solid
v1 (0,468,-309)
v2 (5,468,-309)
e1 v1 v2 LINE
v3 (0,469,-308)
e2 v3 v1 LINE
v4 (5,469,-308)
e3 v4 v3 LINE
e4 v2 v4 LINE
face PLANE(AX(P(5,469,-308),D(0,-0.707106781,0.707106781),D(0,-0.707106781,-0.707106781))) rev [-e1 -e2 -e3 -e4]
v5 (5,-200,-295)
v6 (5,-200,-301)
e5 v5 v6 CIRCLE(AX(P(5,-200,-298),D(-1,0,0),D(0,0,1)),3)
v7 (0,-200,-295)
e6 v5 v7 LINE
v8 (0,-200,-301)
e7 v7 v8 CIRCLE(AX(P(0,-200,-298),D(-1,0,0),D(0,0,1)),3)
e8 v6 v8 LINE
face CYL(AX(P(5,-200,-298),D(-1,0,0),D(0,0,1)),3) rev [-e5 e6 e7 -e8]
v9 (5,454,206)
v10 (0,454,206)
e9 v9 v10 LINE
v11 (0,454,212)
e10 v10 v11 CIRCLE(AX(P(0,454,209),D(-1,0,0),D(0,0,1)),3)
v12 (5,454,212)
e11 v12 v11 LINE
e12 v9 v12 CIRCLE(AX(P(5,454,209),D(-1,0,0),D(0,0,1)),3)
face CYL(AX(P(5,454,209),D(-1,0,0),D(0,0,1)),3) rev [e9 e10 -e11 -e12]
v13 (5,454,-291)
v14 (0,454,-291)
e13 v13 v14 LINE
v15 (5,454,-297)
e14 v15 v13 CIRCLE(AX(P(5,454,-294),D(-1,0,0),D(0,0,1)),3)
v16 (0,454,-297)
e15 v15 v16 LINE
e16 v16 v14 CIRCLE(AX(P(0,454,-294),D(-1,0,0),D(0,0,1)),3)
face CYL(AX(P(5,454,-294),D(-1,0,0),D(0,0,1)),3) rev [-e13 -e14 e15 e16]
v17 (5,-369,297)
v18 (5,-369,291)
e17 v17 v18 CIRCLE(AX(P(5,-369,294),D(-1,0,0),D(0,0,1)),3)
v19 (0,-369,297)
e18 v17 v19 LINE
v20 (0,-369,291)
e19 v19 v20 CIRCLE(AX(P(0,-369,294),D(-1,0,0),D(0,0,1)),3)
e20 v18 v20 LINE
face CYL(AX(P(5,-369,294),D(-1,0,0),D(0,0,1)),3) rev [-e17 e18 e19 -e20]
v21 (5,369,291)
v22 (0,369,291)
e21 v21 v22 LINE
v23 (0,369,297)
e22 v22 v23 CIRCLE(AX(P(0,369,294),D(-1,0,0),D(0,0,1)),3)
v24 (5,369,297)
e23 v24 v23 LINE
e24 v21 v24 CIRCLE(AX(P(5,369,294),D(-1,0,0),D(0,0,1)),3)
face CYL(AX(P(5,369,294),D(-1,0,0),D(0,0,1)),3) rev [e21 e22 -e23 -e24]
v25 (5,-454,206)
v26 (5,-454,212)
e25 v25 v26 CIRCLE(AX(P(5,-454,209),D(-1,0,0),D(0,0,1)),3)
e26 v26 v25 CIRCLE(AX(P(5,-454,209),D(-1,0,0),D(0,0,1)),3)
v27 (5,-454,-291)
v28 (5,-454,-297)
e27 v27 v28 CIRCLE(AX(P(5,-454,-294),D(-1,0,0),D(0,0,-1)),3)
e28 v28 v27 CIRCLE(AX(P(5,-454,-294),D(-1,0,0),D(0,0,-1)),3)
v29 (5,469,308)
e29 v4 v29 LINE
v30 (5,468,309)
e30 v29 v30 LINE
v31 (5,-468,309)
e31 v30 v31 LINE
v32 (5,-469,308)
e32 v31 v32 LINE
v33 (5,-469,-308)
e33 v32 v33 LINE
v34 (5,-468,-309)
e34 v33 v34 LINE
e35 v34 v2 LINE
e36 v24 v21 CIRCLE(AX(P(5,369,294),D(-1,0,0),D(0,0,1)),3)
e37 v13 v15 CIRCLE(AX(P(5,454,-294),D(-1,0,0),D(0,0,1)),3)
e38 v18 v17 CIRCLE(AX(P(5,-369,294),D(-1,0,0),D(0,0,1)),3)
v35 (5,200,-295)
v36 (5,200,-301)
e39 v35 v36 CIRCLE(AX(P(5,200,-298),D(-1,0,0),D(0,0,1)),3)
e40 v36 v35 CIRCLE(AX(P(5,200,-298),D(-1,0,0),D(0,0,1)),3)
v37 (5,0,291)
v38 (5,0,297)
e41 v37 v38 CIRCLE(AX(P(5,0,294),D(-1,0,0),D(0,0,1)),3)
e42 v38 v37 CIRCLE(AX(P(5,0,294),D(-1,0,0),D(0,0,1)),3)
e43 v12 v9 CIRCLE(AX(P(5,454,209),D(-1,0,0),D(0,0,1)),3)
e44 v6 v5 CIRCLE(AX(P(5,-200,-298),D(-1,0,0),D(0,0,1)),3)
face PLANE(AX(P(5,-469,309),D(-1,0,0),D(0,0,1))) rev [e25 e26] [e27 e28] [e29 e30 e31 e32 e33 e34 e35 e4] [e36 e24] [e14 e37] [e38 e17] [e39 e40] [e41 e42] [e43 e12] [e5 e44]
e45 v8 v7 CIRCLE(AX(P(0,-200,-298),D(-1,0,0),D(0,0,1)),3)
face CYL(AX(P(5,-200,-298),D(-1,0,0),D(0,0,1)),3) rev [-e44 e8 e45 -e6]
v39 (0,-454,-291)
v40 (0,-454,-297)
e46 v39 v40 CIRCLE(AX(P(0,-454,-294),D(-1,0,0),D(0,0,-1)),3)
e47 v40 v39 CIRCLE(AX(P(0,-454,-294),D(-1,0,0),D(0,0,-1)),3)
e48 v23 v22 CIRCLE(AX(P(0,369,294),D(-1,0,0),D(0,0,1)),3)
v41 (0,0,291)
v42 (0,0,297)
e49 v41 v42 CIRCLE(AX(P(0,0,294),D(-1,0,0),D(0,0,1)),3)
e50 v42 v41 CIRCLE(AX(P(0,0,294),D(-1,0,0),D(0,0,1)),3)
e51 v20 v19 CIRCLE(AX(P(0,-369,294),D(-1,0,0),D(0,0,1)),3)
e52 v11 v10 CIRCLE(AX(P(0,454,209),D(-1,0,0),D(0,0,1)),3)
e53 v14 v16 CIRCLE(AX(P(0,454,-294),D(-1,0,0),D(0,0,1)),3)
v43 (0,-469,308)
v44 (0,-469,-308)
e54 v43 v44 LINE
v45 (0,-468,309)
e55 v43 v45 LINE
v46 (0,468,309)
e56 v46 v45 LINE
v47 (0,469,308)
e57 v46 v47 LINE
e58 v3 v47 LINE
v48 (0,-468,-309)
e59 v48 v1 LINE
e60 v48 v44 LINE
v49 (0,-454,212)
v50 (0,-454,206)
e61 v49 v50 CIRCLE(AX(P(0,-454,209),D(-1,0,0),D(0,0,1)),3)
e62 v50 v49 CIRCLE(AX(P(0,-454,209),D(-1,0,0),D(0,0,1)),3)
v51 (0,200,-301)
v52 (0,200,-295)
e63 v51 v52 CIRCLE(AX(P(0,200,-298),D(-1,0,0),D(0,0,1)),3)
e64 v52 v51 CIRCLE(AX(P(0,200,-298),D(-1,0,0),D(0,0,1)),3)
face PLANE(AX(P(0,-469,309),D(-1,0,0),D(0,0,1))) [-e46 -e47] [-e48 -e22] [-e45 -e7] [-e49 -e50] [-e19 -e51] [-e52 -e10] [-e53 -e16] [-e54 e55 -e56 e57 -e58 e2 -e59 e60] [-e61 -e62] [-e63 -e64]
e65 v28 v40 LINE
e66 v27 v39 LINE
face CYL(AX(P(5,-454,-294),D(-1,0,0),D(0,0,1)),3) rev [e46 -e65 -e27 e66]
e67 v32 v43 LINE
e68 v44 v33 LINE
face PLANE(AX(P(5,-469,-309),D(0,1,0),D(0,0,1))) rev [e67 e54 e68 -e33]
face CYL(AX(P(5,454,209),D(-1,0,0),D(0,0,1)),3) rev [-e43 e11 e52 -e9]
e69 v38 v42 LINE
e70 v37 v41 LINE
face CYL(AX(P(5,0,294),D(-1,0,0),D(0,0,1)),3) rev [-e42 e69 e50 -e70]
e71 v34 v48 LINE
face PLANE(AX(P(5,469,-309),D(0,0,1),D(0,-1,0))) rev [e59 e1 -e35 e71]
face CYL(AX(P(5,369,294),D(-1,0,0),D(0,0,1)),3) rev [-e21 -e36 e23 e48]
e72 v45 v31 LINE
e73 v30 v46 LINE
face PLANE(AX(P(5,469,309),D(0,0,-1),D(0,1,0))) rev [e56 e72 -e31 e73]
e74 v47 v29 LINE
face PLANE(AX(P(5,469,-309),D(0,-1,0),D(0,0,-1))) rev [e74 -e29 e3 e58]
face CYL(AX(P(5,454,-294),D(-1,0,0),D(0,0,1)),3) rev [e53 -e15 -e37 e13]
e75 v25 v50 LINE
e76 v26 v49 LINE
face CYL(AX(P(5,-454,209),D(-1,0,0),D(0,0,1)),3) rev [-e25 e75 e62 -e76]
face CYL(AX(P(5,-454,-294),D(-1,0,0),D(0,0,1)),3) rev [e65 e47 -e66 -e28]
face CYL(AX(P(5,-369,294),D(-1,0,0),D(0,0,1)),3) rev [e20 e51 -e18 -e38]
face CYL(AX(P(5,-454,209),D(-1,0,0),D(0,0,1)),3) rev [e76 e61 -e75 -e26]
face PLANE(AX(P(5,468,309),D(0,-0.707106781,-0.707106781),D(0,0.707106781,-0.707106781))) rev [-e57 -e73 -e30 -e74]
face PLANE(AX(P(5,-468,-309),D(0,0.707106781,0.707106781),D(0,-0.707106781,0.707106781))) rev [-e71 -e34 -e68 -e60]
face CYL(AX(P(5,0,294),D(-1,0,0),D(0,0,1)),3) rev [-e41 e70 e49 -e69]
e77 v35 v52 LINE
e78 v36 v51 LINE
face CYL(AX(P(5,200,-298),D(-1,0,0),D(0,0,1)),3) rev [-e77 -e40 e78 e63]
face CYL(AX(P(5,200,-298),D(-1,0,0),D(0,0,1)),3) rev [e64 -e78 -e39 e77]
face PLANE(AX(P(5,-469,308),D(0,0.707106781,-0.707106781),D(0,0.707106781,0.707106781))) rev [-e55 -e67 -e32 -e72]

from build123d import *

# Parameters (mm, degrees)
SKETCH_1_W          = 618
SKETCH_1_H          = 938
EXTRUDE_1_DEPTH     = 5
CHAMFER_1_SIZE      = 1
SKETCH_2_R          = 3
CUT_EXTRUDE_1_DEPTH = 562.664490599


with BuildPart() as part:
    # 草图1 → 凸台-拉伸1 (new body)
    with BuildSketch(Plane(origin=(0, 0, 0), x_dir=(0, 0, -1), z_dir=(1, 0, 0))):
        Rectangle(SKETCH_1_W, SKETCH_1_H)
    extrude(amount=EXTRUDE_1_DEPTH)

    # 倒角1
    chamfer_1_edges = [part.edges().sort_by_distance(p)[0] for p in [
        (2.5, 469, 309),
        (2.5, 469, -309),
        (2.5, -469, -309),
        (2.5, -469, 309),
    ]]
    chamfer(chamfer_1_edges, length=CHAMFER_1_SIZE)

    # 草图2 → 切除-拉伸1 (cut, through all)
    with BuildSketch(Plane.ZY):
        with Locations((-294, 454)):
            Circle(SKETCH_2_R)
        with Locations(Location((-294, -454, 0), (0, 0, 180))):
            Circle(SKETCH_2_R)
        with Locations((209, 454)):
            Circle(SKETCH_2_R)
        with Locations((294, 369)):
            Circle(SKETCH_2_R)
        with Locations((294, -369)):
            Circle(SKETCH_2_R)
        with Locations((209, -454)):
            Circle(SKETCH_2_R)
        with Locations((294, 0)):
            Circle(SKETCH_2_R)
        with Locations((-298, 200)):
            Circle(SKETCH_2_R)
        with Locations((-298, -200)):
            Circle(SKETCH_2_R)
    extrude(amount=-CUT_EXTRUDE_1_DEPTH, mode=Mode.SUBTRACT)


solid = part.part
